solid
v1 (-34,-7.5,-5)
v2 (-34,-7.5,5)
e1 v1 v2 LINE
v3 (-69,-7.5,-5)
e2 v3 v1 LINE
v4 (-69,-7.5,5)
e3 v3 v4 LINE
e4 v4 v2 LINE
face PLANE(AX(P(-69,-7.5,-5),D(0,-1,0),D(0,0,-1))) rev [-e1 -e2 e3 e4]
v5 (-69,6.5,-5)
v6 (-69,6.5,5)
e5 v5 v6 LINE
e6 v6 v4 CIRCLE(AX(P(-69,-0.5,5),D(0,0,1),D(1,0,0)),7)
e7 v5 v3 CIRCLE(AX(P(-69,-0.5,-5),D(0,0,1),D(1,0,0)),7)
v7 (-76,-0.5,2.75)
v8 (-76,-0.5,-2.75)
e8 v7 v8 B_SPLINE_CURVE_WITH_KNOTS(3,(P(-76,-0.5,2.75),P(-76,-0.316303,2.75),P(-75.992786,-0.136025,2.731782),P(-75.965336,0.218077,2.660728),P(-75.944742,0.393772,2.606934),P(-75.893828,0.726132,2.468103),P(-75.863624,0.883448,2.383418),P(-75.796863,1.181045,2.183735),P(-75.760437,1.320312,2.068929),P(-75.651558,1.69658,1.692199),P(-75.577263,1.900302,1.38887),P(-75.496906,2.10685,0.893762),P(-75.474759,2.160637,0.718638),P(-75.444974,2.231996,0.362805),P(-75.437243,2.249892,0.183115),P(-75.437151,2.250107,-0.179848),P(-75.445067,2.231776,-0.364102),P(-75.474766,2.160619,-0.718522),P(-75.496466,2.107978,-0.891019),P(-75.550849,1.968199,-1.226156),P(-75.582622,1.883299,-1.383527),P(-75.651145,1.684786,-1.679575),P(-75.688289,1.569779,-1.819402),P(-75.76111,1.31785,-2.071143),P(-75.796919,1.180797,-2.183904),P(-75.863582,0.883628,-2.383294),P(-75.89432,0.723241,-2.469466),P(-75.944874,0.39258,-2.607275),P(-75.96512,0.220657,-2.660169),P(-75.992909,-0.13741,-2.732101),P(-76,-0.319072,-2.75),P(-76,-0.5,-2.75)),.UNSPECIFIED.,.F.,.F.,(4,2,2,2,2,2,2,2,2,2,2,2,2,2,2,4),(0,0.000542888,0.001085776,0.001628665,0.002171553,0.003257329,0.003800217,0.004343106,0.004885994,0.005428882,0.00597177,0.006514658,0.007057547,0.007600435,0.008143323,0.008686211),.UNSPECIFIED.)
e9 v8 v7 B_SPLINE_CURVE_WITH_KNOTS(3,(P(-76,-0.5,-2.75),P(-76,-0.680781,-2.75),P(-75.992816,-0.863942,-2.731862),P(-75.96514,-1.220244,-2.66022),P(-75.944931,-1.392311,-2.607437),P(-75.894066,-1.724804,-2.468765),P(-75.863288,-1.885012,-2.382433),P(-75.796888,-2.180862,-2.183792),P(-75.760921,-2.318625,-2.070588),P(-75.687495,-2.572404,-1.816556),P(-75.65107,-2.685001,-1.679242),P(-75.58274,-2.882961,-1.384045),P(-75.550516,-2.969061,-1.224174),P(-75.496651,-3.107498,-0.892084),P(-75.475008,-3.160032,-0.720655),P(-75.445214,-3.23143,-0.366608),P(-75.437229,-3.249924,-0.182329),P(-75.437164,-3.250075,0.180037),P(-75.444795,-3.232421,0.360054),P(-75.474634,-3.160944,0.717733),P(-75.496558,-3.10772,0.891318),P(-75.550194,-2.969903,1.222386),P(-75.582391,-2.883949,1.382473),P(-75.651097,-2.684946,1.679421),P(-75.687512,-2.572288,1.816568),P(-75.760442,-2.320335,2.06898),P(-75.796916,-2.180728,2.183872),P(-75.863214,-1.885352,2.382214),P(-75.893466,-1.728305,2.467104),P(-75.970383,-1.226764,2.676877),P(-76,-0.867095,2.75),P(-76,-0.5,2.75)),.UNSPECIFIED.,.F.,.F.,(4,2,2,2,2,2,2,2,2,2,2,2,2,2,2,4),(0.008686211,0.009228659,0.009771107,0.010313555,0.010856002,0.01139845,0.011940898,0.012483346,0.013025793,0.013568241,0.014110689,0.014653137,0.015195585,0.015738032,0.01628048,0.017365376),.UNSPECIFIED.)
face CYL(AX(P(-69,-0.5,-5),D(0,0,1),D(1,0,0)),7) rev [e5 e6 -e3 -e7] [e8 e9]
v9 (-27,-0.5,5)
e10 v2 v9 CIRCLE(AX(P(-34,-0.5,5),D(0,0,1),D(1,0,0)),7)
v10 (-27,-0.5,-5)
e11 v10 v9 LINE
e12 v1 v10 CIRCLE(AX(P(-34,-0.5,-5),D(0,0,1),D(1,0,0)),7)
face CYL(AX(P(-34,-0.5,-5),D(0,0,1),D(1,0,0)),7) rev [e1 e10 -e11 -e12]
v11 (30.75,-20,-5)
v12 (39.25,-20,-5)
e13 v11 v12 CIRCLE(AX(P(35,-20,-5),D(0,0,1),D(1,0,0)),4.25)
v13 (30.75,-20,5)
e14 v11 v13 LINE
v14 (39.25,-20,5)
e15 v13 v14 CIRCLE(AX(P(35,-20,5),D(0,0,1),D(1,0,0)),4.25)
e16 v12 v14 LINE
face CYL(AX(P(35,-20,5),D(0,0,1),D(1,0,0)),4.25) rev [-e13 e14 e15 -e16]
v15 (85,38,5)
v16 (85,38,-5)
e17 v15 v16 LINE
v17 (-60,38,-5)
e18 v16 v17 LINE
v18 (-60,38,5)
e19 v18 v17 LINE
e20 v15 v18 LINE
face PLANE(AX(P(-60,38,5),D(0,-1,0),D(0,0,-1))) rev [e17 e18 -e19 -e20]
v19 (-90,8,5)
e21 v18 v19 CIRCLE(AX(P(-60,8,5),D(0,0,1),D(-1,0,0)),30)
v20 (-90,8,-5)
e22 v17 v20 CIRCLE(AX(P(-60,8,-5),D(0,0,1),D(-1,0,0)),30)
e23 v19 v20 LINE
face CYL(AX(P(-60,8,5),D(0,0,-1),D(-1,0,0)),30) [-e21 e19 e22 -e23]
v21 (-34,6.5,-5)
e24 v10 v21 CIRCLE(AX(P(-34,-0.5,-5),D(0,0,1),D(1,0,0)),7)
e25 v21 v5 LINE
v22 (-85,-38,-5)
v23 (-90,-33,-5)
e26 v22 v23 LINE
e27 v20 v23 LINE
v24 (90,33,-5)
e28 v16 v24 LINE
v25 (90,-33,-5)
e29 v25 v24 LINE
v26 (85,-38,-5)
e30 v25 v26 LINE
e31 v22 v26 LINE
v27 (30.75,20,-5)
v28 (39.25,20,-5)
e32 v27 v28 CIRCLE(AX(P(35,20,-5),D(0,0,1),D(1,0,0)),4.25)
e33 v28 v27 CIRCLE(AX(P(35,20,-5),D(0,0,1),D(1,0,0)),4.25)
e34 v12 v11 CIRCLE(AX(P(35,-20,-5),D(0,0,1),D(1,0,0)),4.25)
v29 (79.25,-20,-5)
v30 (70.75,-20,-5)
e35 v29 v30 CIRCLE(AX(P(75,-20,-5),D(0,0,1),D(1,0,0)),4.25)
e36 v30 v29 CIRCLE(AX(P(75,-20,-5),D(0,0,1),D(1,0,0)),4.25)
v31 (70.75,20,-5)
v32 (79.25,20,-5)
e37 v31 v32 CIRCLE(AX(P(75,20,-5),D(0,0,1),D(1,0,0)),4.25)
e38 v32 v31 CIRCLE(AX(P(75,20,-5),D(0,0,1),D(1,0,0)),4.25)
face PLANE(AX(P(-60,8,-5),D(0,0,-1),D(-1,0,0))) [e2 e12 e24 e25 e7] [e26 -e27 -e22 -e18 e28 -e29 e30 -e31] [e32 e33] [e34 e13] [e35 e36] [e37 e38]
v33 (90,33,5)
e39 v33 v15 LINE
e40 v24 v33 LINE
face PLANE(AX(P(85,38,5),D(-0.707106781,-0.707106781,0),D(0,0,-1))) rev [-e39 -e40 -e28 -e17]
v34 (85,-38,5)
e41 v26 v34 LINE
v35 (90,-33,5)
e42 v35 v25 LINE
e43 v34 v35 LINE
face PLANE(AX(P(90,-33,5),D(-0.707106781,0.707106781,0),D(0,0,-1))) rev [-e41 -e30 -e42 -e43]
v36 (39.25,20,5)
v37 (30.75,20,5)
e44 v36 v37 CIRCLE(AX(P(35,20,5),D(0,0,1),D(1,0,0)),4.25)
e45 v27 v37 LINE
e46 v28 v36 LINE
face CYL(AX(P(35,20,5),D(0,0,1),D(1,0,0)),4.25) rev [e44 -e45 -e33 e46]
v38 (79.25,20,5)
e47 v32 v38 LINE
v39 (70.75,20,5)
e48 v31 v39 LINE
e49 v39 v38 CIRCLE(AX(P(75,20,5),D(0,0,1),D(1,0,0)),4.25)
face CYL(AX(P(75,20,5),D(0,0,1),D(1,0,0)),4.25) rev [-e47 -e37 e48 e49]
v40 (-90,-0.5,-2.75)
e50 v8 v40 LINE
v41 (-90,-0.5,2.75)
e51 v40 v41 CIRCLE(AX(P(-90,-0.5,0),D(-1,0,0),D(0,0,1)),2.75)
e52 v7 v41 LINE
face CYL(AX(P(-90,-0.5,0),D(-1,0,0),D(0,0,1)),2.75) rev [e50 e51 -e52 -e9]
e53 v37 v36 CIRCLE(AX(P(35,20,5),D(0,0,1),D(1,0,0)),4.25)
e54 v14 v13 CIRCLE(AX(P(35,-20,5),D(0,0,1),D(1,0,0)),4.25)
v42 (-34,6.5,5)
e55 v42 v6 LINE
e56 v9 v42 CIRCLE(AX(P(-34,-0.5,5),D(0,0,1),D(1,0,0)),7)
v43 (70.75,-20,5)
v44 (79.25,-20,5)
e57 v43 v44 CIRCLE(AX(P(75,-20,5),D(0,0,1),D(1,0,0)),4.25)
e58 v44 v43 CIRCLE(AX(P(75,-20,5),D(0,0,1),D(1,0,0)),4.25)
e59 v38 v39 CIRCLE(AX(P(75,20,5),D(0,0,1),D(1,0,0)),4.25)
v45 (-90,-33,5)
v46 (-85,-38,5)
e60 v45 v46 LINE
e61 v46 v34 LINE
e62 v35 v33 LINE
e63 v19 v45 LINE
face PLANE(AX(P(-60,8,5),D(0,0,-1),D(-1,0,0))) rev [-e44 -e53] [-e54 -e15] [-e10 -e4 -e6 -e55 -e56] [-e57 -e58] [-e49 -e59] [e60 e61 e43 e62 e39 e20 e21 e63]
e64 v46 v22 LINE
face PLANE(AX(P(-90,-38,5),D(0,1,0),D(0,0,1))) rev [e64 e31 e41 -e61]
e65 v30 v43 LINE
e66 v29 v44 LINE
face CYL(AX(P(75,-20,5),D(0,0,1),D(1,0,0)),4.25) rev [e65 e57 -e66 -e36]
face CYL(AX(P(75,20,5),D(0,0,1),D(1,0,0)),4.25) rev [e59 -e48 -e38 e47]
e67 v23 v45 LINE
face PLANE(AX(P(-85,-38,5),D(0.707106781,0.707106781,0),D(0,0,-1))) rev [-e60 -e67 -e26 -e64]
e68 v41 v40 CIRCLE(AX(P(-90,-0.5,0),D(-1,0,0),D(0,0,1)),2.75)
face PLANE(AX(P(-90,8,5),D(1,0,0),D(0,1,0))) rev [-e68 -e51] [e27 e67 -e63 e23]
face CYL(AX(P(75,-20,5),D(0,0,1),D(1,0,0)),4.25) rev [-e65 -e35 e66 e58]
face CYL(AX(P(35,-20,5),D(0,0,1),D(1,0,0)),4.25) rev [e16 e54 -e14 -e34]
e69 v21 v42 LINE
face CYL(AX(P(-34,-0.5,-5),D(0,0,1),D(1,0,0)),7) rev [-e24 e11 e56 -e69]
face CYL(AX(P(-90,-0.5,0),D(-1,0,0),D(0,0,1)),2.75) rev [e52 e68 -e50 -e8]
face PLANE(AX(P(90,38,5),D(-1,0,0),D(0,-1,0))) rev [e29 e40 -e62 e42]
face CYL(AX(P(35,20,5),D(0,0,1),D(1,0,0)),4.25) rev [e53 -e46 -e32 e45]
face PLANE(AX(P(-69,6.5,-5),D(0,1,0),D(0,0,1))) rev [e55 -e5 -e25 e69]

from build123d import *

# Parameters (mm, degrees)
EXTRUDE_1_DEPTH              = 5
HOLE_WIZARD_8_5_8_5_1_D      = 8.5
PATTERN_LINEAR_1_COUNT       = 2
PATTERN_LINEAR_1_PITCH       = 40
MIRROR_1_COPY_1_D            = 8.5
CUT_EXTRUDE_1_DEPTH          = 10
HOLE_WIZARD_5_5_5_5_1_REACH  = 186.035
HOLE_WIZARD_5_5_5_5_1_BORE_R = 2.75
CHAMFER_1_SIZE               = 5


with BuildPart() as part:
    # 草图2 → 凸台-拉伸1 (new, symmetric)
    with BuildSketch(Plane.XY):
        with BuildLine():
            Line((-60, 38), (90, 38))
            Line((90, 38), (90, -38))
            Line((90, -38), (-90, -38))
            Line((-90, -38), (-90, 8))
            ThreePointArc((-90, 8), (-81.213203436, 29.213203436), (-60, 38))
        make_face()
    extrude(amount=EXTRUDE_1_DEPTH, both=True)

    # Ø8.5 (8.5) 直径孔1 (through all)
    with Locations(Plane.XY.offset(5)):
        with Locations((75, 20)):
            hole_wizard_8_5_8_5_1 = Hole(HOLE_WIZARD_8_5_8_5_1_D / 2)

    # 阵列(线性)1: Ø8.5 (8.5) 直径孔1 ×2
    with Locations(*[(-i * PATTERN_LINEAR_1_PITCH, 0, 0) for i in range(1, PATTERN_LINEAR_1_COUNT)]):
        add(hole_wizard_8_5_8_5_1, mode=Mode.SUBTRACT)

    # 镜向1: Ø8.5 (8.5) 直径孔1 across plane
    add(hole_wizard_8_5_8_5_1.mirror(Plane.ZX), mode=Mode.SUBTRACT)

    # 镜向1 copy 1 (through all)
    with Locations(Plane(origin=(-40, 0, 5), x_dir=(1, 0, 0), z_dir=(0, 0, 1))):
        with Locations((75, -20)):
            Hole(MIRROR_1_COPY_1_D / 2)

    # 草图5 → 切除-拉伸1 (cut)
    with BuildSketch(Plane.XY.offset(5)):
        with BuildLine():
            Line((-69, 6.5), (-34, 6.5))
            ThreePointArc((-34, 6.5), (-27, -0.5), (-34, -7.5))
            Line((-34, -7.5), (-69, -7.5))
            ThreePointArc((-69, -7.5), (-76, -0.5), (-69, 6.5))
        make_face()
    extrude(amount=-CUT_EXTRUDE_1_DEPTH, mode=Mode.SUBTRACT)

    # Ø5.5 (5.5) 直径孔1 bore → Ø5.5 (5.5) 直径孔1 (cut, up to next)
    with BuildSketch(Plane.ZY.offset(90), mode=Mode.PRIVATE) as hole_wizard_5_5_5_5_1_sk1:
        with Locations((0, -0.5)):
            Circle(HOLE_WIZARD_5_5_5_5_1_BORE_R)
    hole_wizard_5_5_5_5_1_tool1 = extrude(hole_wizard_5_5_5_5_1_sk1.sketch, amount=-HOLE_WIZARD_5_5_5_5_1_REACH, mode=Mode.PRIVATE) & part.part
    add(hole_wizard_5_5_5_5_1_tool1.solids().sort_by_distance((-90, -0.5, 0))[0], mode=Mode.SUBTRACT)

    # 倒角1
    chamfer_1_edges = [part.edges().sort_by_distance(p)[0] for p in [
        (90, -38, 0),
        (-90, -38, 0),
        (90, 38, 0),
    ]]
    chamfer(chamfer_1_edges, length=CHAMFER_1_SIZE)


solid = part.part
